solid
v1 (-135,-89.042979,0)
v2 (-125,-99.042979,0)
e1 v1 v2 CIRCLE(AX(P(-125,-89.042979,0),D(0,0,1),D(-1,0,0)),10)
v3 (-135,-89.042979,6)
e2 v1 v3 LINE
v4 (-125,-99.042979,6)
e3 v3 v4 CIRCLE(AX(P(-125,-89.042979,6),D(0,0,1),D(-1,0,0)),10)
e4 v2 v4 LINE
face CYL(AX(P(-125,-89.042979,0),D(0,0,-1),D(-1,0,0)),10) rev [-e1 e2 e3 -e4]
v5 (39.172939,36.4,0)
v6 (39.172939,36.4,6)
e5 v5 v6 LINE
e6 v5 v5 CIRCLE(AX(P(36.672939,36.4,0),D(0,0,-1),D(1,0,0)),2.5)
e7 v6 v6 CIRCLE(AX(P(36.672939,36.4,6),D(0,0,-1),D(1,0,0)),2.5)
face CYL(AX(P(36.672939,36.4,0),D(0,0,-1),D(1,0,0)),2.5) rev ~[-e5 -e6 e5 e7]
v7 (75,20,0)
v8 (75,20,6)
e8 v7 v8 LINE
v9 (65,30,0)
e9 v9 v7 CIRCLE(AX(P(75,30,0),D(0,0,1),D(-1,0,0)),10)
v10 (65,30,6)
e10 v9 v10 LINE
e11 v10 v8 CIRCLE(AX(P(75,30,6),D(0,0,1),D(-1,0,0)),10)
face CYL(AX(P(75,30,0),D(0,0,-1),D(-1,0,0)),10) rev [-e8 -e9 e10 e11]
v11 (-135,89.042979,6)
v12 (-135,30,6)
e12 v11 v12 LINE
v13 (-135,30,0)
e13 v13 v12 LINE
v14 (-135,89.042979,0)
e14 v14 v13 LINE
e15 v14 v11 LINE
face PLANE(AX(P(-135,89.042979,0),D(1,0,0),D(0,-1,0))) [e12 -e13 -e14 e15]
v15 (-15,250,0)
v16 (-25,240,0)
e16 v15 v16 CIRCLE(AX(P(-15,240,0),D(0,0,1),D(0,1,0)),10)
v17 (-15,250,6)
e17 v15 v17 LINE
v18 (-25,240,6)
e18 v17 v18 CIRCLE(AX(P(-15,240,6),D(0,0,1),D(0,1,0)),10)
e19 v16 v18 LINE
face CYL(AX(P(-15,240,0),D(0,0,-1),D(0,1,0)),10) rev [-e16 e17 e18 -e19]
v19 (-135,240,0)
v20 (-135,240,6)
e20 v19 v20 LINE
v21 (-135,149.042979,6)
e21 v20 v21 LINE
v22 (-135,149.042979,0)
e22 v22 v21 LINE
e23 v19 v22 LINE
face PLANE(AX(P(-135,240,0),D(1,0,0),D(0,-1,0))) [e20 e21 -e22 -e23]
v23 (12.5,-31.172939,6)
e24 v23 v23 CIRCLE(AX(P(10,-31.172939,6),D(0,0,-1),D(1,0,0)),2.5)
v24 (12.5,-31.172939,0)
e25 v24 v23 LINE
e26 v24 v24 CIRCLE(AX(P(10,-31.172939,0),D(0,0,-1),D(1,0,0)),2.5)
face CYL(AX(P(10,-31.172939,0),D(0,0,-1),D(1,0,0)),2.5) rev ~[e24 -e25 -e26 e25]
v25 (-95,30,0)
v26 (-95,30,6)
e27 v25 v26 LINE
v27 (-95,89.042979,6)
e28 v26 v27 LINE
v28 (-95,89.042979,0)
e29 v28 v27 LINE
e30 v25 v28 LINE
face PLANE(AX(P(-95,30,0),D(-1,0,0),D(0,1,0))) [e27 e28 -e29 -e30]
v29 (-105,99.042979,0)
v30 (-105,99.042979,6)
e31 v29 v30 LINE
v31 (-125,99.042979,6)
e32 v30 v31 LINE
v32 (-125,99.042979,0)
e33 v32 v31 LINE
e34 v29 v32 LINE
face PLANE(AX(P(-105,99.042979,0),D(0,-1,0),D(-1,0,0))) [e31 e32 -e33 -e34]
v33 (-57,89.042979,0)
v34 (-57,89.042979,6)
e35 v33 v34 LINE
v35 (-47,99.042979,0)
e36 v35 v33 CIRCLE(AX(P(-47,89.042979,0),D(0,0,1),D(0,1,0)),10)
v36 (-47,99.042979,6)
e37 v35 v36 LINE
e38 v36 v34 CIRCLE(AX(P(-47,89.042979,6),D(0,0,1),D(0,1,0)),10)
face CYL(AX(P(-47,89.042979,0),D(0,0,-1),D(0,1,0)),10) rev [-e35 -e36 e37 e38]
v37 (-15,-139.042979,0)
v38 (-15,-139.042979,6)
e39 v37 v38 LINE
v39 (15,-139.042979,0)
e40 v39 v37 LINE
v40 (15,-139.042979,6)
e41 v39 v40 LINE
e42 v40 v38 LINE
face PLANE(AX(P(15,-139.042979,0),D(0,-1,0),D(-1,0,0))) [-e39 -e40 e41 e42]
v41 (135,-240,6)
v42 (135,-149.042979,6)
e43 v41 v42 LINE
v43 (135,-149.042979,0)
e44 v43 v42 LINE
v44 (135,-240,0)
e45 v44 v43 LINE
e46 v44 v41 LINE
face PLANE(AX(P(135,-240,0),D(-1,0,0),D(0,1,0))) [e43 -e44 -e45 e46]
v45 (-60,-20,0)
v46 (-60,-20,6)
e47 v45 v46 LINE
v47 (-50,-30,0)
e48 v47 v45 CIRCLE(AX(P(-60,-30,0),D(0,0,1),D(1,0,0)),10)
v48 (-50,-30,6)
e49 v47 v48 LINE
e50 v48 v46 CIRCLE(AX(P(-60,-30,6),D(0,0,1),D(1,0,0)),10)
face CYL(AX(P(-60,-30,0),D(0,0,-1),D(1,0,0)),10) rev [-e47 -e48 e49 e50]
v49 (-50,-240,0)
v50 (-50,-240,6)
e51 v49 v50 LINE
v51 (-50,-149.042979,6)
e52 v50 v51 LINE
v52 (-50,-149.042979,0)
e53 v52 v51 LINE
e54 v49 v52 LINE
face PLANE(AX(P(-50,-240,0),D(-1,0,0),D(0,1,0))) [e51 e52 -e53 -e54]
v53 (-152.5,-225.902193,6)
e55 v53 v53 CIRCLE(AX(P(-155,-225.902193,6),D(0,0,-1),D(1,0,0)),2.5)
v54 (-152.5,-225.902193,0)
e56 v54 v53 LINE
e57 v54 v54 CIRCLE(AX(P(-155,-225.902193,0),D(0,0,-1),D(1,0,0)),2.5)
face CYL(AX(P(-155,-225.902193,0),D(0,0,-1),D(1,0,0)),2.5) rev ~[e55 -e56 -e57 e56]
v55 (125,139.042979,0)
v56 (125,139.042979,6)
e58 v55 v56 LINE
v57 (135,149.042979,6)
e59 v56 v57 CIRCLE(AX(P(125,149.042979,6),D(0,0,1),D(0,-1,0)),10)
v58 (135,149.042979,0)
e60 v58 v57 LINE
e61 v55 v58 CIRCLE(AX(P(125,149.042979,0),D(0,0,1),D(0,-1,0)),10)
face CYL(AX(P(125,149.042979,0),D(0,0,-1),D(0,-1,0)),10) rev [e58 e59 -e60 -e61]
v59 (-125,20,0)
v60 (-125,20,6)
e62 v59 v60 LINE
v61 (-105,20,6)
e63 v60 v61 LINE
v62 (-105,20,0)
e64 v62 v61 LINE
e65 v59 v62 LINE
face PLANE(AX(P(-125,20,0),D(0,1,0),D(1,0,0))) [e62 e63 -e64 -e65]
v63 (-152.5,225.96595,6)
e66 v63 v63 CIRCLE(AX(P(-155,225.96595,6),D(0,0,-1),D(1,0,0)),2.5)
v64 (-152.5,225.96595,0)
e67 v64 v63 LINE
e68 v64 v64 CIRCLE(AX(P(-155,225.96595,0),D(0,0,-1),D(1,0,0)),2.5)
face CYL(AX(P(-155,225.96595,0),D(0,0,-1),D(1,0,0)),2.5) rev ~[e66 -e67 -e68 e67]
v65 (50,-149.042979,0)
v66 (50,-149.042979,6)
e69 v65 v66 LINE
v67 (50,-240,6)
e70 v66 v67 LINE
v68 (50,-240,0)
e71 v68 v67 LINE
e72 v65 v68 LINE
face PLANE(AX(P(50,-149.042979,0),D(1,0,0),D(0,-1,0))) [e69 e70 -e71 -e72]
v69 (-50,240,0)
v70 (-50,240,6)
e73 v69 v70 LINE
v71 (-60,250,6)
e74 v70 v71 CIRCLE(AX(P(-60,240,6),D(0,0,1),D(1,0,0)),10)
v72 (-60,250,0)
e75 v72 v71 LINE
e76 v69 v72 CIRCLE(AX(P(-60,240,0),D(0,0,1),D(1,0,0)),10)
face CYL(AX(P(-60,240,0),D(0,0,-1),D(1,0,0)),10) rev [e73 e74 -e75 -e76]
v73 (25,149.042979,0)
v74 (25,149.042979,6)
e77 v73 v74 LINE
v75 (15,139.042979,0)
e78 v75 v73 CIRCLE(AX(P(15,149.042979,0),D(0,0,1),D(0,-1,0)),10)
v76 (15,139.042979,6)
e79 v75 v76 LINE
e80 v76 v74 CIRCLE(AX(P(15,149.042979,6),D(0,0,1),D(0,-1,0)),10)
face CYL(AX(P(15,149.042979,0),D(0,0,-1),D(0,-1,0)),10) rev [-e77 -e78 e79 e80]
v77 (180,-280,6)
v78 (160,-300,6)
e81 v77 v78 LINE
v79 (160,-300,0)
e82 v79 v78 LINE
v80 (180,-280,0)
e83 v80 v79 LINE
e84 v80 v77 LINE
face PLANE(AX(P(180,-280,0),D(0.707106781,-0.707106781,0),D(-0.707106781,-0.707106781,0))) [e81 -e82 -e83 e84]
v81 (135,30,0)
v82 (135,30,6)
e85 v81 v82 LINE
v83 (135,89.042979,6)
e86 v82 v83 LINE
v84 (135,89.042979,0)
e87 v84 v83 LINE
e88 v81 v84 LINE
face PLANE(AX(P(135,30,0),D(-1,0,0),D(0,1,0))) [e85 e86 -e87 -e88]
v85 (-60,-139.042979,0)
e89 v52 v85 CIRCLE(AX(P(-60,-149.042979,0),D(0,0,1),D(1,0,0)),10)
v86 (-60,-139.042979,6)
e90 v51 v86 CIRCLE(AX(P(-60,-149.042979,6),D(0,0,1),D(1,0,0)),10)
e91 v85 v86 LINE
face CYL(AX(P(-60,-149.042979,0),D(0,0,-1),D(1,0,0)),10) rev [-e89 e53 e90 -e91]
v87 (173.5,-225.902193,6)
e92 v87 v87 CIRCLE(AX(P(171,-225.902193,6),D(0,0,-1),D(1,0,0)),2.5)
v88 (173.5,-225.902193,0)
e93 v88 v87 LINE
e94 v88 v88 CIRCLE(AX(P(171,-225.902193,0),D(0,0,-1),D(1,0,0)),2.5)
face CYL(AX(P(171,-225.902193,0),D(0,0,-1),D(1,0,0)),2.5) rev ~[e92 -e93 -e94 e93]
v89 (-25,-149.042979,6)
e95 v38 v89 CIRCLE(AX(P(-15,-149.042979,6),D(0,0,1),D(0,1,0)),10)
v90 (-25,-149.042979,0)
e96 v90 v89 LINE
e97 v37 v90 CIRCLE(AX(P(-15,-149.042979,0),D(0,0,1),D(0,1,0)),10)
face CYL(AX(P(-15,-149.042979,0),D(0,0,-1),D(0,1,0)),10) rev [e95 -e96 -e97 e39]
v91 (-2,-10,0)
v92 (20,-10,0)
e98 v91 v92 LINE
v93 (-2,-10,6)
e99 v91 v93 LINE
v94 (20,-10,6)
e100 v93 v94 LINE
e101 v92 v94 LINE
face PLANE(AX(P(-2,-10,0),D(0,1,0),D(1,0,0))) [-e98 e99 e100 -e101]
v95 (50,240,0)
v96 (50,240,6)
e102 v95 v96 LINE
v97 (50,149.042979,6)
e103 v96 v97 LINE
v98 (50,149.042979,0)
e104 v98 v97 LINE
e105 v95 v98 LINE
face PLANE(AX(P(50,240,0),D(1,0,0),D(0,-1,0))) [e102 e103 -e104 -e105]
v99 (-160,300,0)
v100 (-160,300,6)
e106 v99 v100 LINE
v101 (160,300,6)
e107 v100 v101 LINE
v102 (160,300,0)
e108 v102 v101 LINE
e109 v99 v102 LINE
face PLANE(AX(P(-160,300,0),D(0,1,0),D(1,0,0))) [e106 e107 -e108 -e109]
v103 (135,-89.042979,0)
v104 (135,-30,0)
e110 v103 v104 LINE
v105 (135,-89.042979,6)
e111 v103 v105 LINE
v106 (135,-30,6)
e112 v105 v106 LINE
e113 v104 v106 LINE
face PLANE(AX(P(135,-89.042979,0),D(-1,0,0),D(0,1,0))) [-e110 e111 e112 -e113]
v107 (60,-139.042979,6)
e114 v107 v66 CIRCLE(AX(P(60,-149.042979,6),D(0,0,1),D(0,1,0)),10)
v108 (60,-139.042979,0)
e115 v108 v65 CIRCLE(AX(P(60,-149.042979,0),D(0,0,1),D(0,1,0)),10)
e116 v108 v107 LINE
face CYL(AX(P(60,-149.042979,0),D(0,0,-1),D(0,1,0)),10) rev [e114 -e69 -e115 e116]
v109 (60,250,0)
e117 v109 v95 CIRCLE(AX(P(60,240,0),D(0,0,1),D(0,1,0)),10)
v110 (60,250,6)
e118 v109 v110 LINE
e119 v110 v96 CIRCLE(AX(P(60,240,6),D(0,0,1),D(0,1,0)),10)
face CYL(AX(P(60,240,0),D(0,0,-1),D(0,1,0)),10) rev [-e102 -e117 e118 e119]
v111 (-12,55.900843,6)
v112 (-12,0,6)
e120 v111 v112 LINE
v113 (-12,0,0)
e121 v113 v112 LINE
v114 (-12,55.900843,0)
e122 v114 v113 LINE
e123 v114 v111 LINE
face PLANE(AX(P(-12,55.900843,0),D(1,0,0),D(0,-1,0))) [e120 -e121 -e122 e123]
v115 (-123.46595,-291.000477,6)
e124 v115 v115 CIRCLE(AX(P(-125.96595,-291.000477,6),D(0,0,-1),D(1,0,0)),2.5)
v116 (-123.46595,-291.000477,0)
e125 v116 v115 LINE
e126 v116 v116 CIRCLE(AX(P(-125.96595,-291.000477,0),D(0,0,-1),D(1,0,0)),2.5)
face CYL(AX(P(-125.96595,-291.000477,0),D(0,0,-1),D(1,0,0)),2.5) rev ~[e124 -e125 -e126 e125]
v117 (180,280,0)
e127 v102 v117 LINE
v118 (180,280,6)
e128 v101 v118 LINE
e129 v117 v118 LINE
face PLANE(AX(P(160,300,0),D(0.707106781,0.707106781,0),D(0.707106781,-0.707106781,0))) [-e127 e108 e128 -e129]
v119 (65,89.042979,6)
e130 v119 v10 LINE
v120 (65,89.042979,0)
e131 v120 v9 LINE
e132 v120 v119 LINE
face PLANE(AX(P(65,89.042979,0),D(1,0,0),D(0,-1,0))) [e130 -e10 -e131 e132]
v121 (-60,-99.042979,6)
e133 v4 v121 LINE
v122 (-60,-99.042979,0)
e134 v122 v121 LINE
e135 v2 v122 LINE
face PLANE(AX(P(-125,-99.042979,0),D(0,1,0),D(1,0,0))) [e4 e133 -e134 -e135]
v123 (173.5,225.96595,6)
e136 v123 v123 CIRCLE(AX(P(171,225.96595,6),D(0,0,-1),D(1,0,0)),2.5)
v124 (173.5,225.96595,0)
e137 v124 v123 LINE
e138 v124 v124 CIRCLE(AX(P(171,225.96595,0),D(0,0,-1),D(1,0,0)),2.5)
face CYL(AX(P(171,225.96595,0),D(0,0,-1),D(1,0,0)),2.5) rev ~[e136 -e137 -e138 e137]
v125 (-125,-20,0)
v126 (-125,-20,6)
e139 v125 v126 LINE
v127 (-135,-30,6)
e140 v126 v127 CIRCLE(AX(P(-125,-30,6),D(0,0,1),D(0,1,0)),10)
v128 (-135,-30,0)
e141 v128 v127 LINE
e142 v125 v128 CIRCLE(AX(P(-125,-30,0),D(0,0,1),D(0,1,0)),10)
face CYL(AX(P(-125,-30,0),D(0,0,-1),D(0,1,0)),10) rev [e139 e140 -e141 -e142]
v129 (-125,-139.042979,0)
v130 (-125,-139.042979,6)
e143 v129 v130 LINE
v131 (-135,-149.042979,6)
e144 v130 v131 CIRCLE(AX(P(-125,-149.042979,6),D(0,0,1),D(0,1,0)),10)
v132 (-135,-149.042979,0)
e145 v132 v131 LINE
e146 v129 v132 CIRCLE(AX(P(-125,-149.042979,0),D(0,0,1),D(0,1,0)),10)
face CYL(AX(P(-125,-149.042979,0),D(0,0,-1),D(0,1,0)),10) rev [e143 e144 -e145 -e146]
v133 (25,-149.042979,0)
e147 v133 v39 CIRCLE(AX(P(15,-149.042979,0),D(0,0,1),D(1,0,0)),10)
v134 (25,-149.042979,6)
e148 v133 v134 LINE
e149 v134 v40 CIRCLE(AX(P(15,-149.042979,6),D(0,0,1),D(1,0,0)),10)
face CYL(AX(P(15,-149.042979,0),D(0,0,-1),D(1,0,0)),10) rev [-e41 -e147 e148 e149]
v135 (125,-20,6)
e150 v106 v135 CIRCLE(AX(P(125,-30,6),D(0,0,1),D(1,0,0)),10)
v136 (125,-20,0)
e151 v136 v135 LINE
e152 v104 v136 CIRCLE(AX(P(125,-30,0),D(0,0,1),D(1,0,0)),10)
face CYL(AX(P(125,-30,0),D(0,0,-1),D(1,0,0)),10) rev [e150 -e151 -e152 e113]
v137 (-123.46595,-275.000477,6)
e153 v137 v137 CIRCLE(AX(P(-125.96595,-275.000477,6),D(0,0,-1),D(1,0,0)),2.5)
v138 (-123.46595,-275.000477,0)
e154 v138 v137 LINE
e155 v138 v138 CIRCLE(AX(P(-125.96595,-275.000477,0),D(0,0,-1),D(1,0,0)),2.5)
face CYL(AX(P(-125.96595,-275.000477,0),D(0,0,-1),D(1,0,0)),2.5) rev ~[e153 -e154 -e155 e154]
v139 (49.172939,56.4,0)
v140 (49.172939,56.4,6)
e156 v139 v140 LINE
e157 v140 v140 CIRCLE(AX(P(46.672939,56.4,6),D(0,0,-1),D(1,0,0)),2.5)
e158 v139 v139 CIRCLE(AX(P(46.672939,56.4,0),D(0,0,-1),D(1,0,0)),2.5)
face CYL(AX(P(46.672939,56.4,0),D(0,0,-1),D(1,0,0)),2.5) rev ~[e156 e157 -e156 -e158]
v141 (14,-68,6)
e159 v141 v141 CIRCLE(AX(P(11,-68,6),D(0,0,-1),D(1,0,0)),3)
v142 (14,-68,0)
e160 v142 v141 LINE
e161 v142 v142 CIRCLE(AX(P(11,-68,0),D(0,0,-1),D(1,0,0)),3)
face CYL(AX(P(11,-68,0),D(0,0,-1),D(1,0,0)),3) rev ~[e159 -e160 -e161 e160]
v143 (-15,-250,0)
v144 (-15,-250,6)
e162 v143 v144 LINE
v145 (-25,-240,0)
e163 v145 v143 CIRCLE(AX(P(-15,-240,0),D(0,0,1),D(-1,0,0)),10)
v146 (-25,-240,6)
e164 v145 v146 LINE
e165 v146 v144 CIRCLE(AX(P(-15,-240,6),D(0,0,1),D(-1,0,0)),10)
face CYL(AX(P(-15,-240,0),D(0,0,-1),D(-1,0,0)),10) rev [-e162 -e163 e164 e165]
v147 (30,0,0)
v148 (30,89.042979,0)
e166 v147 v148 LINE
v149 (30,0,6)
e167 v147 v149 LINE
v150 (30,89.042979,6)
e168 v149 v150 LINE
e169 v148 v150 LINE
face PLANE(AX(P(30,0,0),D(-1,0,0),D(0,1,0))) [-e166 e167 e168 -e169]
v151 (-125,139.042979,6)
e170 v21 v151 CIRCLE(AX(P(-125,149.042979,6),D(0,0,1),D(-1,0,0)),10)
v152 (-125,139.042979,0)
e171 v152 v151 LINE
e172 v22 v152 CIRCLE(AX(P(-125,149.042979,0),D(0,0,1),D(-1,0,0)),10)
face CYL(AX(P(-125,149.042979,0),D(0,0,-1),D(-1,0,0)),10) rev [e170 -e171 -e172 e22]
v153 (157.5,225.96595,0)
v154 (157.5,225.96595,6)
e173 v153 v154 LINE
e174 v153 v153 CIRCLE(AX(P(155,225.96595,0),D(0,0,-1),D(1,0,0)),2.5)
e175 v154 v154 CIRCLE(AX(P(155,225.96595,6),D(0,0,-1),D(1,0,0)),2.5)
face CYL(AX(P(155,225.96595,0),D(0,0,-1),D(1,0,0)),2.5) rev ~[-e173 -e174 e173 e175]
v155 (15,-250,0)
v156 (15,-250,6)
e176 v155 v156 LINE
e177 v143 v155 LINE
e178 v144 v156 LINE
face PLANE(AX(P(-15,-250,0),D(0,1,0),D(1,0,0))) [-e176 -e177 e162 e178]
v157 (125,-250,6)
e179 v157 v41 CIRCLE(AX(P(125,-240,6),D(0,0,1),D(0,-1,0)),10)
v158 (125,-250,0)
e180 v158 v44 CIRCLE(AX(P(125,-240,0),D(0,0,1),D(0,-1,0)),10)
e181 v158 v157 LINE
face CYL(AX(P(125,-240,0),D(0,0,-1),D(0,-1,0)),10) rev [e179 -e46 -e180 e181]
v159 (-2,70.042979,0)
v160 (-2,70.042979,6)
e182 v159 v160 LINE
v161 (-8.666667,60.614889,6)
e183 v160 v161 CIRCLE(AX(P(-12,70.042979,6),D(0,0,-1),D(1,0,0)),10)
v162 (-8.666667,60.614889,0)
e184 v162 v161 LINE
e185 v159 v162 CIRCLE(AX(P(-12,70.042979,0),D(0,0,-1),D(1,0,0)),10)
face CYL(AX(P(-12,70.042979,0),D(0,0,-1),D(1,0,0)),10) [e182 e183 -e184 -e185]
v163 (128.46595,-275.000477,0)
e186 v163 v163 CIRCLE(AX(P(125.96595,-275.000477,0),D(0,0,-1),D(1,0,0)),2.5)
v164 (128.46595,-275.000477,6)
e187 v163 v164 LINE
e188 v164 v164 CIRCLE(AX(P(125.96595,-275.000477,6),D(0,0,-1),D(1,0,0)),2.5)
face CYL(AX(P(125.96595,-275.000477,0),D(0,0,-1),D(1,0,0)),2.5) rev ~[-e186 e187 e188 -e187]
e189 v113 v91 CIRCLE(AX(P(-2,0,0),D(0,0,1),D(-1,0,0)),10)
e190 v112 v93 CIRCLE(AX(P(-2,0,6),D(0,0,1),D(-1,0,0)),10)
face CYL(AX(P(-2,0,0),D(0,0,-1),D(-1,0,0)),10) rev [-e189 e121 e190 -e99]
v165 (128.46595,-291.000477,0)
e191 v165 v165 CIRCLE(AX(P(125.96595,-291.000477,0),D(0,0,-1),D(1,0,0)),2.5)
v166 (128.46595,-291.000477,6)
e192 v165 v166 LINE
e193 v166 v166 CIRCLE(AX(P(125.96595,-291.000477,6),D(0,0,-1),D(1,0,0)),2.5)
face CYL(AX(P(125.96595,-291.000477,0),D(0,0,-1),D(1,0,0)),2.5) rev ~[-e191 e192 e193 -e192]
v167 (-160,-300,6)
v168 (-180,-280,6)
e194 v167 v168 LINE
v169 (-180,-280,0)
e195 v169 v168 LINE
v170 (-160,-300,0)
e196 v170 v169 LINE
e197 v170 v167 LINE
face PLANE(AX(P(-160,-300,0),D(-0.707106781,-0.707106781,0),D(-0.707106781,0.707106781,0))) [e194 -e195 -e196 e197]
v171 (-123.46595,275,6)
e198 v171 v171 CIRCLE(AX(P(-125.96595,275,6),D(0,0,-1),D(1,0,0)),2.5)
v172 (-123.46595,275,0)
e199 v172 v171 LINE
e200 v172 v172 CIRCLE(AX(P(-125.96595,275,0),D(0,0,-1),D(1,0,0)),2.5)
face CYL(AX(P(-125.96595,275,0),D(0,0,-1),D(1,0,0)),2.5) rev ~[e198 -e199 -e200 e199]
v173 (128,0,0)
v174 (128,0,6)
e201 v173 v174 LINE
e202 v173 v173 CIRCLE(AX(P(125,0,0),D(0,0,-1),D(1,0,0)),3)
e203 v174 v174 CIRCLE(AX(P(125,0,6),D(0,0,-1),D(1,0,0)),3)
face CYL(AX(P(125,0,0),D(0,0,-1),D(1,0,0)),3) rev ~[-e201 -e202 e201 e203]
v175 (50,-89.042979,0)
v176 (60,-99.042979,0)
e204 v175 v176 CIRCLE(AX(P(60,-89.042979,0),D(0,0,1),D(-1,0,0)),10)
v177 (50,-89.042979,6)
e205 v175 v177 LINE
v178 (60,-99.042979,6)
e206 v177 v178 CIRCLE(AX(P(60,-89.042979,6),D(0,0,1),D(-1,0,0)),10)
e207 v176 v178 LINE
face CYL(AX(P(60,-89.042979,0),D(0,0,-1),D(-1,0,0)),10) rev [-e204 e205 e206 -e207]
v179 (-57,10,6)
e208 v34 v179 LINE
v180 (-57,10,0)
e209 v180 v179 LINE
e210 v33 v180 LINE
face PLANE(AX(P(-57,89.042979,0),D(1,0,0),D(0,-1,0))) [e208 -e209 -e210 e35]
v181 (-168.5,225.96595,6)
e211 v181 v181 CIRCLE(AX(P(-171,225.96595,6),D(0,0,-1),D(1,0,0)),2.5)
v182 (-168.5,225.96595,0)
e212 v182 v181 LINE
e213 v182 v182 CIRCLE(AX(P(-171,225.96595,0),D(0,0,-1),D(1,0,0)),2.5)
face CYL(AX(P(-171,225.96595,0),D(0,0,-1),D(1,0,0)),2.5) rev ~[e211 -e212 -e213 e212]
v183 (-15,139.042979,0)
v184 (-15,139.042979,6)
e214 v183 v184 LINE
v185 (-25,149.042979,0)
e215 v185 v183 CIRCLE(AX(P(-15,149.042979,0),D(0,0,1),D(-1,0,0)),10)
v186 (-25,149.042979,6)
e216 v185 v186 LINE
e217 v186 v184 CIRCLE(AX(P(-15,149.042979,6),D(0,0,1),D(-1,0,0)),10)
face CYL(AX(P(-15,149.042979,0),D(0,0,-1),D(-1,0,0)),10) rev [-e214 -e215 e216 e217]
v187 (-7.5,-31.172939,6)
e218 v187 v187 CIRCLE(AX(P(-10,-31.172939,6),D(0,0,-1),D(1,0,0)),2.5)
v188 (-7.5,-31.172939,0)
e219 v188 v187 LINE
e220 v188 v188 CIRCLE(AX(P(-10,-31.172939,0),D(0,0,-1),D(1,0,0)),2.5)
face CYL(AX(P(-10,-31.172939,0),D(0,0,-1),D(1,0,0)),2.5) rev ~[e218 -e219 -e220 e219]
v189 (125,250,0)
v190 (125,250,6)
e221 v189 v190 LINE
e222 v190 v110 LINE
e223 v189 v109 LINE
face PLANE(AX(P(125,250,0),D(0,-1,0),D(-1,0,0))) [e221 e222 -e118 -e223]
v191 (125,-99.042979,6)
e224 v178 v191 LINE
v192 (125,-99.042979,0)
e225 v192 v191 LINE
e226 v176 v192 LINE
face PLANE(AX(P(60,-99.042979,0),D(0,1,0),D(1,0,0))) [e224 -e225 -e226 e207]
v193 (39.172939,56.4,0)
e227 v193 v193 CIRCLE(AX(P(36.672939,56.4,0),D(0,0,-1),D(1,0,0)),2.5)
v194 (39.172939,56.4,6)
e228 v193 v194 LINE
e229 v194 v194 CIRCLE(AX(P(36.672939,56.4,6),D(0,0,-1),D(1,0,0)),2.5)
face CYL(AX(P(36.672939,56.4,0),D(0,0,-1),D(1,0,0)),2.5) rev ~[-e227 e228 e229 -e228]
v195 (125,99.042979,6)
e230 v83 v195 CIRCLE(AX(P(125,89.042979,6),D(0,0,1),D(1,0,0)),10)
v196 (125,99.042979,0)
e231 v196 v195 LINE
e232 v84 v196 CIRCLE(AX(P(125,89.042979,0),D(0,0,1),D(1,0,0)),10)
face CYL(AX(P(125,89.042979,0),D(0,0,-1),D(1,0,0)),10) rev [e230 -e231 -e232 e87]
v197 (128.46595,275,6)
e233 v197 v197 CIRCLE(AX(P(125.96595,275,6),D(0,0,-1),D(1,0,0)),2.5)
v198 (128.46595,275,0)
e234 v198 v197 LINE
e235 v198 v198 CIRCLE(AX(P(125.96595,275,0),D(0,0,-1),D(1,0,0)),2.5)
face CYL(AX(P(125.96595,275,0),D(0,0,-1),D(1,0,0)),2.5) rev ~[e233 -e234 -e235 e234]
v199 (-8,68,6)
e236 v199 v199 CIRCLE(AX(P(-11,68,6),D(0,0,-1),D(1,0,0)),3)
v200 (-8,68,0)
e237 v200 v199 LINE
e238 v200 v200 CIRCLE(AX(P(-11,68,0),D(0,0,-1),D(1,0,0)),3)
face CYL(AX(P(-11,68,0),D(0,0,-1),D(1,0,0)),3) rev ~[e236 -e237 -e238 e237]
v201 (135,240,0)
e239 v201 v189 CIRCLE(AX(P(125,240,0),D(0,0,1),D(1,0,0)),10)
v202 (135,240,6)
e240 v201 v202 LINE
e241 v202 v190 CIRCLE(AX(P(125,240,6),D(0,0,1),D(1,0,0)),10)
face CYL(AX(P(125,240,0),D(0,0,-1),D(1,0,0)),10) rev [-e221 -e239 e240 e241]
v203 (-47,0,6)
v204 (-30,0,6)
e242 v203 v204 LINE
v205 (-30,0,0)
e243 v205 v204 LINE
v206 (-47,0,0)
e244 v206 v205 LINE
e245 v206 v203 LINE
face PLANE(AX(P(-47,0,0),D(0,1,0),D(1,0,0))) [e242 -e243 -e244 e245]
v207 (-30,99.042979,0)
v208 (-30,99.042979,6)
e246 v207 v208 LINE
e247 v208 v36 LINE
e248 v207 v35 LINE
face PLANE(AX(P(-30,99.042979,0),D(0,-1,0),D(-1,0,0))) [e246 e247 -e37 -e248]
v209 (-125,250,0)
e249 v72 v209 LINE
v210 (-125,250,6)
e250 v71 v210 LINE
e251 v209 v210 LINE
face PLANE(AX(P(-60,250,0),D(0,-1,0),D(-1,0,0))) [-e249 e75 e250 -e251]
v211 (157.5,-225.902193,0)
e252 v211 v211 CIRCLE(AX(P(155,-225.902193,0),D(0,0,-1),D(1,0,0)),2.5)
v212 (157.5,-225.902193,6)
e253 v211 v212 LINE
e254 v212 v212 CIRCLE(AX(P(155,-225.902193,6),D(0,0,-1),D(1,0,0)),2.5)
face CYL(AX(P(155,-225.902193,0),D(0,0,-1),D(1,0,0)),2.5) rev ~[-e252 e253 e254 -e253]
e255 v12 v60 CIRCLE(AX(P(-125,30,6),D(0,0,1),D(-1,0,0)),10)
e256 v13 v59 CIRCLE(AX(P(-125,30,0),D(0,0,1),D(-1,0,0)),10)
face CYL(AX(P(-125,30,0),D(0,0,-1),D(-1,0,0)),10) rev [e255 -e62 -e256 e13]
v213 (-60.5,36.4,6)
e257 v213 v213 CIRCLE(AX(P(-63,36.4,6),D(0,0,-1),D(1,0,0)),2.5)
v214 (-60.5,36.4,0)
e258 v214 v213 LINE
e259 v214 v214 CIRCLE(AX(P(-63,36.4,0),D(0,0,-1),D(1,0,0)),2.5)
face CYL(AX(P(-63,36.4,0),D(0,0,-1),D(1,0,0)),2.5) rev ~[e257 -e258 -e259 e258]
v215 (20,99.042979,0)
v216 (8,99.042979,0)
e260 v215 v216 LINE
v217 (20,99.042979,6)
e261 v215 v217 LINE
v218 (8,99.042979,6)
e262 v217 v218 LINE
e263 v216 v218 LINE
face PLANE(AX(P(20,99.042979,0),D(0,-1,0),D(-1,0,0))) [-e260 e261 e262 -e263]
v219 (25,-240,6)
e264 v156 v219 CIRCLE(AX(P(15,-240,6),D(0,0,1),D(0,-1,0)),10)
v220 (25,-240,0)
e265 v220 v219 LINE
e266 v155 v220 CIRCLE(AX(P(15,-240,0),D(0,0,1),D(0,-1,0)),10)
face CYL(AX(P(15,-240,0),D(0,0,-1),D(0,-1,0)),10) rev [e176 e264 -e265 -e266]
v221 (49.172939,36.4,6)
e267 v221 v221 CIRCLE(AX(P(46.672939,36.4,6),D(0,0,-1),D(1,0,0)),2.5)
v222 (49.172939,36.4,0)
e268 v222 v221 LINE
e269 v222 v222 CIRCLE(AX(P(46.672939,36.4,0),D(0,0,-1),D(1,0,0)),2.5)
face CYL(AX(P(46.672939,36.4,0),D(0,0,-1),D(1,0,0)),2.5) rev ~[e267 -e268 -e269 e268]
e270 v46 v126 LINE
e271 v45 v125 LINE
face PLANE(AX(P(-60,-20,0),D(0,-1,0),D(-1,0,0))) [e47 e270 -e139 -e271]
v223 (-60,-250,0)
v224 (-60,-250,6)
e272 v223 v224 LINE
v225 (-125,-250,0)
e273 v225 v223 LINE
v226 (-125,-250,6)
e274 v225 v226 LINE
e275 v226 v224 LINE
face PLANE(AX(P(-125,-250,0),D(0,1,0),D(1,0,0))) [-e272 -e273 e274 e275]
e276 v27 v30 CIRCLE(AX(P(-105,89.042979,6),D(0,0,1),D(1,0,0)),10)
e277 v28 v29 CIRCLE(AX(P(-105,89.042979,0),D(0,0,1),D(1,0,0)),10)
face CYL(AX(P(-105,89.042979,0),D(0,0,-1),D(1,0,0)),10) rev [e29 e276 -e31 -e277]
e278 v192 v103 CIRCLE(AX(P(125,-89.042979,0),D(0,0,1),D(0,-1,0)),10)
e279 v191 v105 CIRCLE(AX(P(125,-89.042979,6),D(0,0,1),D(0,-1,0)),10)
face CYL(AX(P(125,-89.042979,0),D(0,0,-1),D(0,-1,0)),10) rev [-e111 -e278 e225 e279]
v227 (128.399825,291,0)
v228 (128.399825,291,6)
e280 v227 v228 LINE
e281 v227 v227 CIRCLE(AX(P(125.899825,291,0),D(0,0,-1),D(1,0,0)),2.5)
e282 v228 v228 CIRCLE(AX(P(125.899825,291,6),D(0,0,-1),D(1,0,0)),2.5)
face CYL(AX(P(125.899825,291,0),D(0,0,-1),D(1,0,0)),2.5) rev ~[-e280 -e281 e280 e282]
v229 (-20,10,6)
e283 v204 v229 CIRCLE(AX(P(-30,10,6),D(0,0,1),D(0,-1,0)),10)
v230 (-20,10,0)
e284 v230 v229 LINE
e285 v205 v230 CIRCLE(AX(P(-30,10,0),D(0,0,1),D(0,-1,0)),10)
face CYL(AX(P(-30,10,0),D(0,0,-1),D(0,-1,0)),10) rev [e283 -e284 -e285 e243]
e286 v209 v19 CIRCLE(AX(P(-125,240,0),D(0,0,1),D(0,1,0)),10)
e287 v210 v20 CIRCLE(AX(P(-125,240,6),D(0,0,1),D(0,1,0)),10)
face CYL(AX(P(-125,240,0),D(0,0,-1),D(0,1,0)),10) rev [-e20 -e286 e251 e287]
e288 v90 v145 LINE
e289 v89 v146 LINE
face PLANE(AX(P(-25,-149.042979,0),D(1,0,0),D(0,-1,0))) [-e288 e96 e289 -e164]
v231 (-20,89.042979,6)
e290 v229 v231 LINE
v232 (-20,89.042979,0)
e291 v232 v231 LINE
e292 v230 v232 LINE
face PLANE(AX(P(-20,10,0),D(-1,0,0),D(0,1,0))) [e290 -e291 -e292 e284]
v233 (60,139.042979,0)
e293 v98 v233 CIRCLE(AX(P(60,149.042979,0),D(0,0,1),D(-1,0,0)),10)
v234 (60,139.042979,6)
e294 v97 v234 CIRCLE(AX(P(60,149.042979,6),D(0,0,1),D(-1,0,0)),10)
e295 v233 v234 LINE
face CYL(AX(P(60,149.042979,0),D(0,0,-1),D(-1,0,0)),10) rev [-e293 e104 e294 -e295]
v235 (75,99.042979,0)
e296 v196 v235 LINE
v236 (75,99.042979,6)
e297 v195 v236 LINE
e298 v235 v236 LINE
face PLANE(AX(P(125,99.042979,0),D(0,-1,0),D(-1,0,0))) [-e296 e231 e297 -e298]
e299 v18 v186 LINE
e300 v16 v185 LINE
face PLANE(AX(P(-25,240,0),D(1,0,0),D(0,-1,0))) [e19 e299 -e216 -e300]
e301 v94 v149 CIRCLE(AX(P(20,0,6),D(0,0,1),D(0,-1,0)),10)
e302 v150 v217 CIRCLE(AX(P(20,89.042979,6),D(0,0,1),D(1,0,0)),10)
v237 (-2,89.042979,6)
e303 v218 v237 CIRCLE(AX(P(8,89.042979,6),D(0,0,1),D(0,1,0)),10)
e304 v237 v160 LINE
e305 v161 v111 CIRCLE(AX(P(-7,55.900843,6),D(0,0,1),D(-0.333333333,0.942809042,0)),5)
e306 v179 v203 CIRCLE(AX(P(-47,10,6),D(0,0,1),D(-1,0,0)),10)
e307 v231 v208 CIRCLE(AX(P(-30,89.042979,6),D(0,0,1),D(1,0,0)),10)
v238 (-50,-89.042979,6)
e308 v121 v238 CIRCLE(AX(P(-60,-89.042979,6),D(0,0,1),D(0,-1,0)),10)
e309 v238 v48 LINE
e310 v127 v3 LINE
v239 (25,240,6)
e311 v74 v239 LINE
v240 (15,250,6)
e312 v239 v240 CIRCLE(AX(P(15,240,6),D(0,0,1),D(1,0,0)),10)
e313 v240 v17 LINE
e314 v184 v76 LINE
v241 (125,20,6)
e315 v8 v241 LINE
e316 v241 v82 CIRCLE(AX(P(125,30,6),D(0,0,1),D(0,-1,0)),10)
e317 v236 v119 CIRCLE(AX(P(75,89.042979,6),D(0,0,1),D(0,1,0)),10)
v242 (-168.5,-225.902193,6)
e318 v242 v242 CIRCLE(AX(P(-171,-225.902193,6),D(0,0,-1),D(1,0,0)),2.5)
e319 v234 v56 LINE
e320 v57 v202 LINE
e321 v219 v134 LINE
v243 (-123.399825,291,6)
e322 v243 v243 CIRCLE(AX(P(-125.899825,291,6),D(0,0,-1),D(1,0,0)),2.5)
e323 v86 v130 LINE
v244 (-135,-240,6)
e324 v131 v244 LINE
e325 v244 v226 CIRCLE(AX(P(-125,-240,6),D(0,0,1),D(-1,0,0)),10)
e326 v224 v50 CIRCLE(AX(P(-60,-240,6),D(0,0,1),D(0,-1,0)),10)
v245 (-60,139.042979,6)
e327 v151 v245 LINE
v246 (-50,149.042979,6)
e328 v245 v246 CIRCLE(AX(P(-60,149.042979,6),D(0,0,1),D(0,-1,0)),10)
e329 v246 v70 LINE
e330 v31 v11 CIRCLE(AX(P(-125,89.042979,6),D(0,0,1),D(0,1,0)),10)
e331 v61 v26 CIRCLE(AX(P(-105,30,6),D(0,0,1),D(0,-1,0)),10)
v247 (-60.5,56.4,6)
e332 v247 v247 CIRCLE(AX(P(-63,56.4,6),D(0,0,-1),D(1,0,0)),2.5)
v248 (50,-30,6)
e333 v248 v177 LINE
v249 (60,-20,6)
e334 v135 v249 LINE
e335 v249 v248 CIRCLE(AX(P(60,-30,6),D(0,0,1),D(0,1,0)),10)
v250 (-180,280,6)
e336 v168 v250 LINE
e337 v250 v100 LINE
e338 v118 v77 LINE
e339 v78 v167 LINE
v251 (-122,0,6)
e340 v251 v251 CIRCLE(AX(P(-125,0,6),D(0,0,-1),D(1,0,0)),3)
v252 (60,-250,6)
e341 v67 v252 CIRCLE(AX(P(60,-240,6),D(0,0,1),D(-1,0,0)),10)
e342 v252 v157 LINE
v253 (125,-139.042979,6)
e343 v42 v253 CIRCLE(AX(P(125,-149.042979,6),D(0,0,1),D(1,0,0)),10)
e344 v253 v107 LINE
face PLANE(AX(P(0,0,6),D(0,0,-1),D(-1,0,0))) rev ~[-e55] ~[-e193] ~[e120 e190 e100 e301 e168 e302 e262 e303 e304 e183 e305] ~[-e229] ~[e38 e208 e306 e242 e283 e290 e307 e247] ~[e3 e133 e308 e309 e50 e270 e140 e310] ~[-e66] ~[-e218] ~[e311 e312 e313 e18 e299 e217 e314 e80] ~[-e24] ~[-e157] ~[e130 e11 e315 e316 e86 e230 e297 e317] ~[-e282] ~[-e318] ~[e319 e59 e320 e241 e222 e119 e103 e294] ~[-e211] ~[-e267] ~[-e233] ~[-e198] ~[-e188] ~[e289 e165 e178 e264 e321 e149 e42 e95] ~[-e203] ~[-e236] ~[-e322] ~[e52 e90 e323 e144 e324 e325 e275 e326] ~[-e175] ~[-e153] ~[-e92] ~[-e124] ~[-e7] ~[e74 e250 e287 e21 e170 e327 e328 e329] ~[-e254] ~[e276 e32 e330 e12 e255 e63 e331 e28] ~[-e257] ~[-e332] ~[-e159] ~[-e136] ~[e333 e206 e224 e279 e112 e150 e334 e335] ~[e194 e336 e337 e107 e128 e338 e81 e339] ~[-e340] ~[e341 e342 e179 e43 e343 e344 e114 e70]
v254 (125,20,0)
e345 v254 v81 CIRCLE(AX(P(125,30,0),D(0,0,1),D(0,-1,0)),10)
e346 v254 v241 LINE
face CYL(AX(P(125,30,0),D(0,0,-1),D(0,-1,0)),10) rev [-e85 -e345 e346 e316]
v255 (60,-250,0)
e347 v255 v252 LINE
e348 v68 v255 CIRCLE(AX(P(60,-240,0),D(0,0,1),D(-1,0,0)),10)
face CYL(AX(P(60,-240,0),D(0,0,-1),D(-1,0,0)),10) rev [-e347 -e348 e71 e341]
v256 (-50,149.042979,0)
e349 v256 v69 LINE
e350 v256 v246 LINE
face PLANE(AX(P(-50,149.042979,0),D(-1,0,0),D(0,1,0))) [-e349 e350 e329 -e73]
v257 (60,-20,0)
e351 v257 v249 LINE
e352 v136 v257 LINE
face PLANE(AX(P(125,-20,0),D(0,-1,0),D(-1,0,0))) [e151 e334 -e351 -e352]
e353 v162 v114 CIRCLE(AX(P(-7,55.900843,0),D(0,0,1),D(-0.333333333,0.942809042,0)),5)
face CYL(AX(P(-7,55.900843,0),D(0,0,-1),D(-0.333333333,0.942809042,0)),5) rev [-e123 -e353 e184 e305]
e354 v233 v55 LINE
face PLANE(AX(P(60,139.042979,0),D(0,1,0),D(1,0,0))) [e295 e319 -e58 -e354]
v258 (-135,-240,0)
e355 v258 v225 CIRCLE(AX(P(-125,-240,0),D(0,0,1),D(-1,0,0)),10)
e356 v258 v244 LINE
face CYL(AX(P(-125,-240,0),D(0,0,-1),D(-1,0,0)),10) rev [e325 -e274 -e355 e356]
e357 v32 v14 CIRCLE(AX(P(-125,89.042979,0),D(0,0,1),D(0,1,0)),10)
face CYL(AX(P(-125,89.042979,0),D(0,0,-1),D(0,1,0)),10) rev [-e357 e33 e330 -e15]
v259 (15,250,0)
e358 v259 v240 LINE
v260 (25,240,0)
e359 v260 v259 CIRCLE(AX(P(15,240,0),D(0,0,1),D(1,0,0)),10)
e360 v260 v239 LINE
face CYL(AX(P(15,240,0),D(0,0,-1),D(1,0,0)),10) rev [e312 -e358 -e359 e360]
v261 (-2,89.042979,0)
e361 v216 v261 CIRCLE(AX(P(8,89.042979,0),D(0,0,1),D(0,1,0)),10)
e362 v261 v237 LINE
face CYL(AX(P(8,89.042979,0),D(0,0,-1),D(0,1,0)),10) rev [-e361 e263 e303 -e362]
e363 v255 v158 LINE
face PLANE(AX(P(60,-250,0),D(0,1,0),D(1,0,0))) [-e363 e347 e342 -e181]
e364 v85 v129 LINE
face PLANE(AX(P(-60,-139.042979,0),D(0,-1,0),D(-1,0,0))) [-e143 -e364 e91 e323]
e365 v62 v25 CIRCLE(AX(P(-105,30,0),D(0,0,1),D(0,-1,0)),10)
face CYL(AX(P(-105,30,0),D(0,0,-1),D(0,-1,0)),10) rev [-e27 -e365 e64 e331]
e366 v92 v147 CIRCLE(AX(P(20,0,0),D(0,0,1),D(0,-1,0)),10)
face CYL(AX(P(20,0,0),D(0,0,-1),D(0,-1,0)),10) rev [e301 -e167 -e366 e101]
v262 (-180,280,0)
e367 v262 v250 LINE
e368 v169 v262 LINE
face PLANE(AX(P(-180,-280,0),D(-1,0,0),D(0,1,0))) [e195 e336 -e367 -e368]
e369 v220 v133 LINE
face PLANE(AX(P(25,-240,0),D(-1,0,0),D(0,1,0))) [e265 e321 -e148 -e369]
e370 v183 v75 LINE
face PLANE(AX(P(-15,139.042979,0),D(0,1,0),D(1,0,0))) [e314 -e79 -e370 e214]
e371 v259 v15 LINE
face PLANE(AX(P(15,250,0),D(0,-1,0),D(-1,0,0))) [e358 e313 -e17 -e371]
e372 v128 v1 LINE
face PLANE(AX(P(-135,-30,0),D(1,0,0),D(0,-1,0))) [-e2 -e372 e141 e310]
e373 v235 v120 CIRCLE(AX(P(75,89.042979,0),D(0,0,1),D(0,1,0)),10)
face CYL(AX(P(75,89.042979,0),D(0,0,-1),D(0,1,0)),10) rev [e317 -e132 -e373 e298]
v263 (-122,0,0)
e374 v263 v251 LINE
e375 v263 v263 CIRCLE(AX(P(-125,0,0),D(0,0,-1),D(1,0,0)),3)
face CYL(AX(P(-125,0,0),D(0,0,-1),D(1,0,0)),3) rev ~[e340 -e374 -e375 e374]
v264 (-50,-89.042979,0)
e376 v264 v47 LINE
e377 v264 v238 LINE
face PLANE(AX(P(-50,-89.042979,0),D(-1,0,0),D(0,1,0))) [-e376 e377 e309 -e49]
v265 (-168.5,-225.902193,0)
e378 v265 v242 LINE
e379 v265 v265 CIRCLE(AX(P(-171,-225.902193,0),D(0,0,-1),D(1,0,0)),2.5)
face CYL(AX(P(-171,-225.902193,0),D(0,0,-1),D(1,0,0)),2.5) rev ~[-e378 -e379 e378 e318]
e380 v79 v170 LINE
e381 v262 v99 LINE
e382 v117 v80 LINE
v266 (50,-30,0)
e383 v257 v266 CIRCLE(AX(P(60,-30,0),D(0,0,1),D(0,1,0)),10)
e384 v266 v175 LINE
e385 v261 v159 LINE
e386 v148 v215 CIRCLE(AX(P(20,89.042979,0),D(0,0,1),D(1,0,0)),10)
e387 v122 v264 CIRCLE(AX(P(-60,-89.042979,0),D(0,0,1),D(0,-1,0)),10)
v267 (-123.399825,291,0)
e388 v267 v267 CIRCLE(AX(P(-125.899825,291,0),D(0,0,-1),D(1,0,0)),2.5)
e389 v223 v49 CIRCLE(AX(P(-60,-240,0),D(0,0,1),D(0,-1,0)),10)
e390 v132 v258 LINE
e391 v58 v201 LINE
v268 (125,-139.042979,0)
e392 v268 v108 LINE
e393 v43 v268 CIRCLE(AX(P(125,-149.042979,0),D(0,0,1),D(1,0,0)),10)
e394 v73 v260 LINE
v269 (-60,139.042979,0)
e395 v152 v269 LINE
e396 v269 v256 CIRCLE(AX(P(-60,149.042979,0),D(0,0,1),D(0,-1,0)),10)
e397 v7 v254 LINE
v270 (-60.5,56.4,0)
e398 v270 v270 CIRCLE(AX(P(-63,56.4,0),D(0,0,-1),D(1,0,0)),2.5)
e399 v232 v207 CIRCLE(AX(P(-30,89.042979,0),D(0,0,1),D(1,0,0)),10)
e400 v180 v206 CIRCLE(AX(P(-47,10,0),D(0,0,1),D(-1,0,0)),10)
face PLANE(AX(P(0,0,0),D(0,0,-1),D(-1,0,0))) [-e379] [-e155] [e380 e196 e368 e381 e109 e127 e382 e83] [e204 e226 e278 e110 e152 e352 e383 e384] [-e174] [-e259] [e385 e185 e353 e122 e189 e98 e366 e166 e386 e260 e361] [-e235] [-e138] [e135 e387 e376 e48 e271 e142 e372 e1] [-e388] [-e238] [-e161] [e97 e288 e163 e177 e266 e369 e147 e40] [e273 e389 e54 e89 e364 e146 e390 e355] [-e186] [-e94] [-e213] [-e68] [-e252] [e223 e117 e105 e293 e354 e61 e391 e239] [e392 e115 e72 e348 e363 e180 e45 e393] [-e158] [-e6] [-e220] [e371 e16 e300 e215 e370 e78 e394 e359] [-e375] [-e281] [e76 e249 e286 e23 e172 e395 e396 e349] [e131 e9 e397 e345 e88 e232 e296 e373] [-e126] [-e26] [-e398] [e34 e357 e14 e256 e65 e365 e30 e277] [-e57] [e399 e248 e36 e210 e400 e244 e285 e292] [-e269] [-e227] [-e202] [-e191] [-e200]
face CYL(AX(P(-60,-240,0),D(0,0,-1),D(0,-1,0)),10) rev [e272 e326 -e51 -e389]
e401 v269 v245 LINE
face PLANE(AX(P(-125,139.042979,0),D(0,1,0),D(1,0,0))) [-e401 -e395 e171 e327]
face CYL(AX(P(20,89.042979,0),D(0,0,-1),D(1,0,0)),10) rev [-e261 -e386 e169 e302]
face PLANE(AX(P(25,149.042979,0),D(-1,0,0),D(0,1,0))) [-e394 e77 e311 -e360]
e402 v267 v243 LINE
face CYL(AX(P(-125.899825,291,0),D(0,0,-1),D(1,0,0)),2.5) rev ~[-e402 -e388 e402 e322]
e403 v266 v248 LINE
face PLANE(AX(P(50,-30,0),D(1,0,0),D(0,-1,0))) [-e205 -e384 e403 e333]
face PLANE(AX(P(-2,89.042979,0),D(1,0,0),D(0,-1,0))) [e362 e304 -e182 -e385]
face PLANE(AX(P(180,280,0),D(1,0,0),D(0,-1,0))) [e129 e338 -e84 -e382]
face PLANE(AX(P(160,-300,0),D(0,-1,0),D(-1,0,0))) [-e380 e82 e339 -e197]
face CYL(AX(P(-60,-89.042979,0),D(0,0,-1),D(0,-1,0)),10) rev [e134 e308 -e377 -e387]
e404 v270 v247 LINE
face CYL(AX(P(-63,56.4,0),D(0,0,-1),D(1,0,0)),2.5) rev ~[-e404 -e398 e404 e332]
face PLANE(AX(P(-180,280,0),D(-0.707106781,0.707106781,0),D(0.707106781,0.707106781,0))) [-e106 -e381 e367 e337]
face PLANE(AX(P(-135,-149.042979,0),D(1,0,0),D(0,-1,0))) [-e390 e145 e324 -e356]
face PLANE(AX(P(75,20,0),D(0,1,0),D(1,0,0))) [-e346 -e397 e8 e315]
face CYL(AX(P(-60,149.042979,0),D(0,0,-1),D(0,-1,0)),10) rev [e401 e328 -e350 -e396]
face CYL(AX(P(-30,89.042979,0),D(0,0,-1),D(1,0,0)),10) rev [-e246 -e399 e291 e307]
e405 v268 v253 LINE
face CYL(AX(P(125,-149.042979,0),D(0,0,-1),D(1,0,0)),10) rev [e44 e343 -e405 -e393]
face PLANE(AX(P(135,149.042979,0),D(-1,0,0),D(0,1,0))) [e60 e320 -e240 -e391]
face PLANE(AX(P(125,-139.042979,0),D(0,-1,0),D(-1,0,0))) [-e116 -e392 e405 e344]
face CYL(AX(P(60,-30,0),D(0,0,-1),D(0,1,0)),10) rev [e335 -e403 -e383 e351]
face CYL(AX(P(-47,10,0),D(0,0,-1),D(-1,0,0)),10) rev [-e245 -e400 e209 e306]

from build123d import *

# Parameters (mm, degrees)
SKETCH_1_R      = 2.5
SKETCH_1_R_2    = 3
EXTRUDE_1_DEPTH = 6


with BuildPart() as part:
    # 草图1 → 凸台-拉伸1 (new body)
    with BuildSketch(Plane(origin=(0, 0, 0), x_dir=(-1, 0, 0), z_dir=(0, 0, -1))):
        Polygon((160, -300), (180, -280), (180, 280), (160, 300), (-160, 300), (-180, 280), (-180, -280), (-160, -300), align=None)
        with Locations(Location((-36.672939041, 56.4, 0), (0, 0, 180))):
            Circle(SKETCH_1_R, mode=Mode.SUBTRACT)
        with Locations(Location((-10, -31.172939041, 0), (0, 0, 180))):
            Circle(SKETCH_1_R, mode=Mode.SUBTRACT)
        with Locations(Location((10, -31.172939041, 0), (0, 0, 180))):
            Circle(SKETCH_1_R, mode=Mode.SUBTRACT)
        with Locations(Location((-171, 225.965949669, 0), (0, 0, 180))):
            Circle(SKETCH_1_R, mode=Mode.SUBTRACT)
        with Locations(Location((-155, 225.965949669, 0), (0, 0, 180))):
            Circle(SKETCH_1_R, mode=Mode.SUBTRACT)
        with Locations(Location((-125.965949669, 275, 0), (0, 0, 180))):
            Circle(SKETCH_1_R, mode=Mode.SUBTRACT)
        with Locations(Location((-125.899824793, 291, 0), (0, 0, 180))):
            Circle(SKETCH_1_R, mode=Mode.SUBTRACT)
        with Locations(Location((-171, -225.902192547, 0), (0, 0, 180))):
            Circle(SKETCH_1_R, mode=Mode.SUBTRACT)
        with Locations(Location((-155, -225.902192547, 0), (0, 0, 180))):
            Circle(SKETCH_1_R, mode=Mode.SUBTRACT)
        with Locations(Location((-125.965949669, -275.000477451, 0), (0, 0, 180))):
            Circle(SKETCH_1_R, mode=Mode.SUBTRACT)
        with Locations(Location((-125.965949669, -291.000477451, 0), (0, 0, 180))):
            Circle(SKETCH_1_R, mode=Mode.SUBTRACT)
        with Locations(Location((125.899824793, 291, 0), (0, 0, 180))):
            Circle(SKETCH_1_R, mode=Mode.SUBTRACT)
        with Locations(Location((125.965949669, 275, 0), (0, 0, 180))):
            Circle(SKETCH_1_R, mode=Mode.SUBTRACT)
        with Locations(Location((171, 225.965949669, 0), (0, 0, 180))):
            Circle(SKETCH_1_R, mode=Mode.SUBTRACT)
        with Locations(Location((155, 225.965949669, 0), (0, 0, 180))):
            Circle(SKETCH_1_R, mode=Mode.SUBTRACT)
        with Locations(Location((171, -225.902192547, 0), (0, 0, 180))):
            Circle(SKETCH_1_R, mode=Mode.SUBTRACT)
        with Locations(Location((155, -225.902192547, 0), (0, 0, 180))):
            Circle(SKETCH_1_R, mode=Mode.SUBTRACT)
        with Locations(Location((125.965949669, -291.000477451, 0), (0, 0, 180))):
            Circle(SKETCH_1_R, mode=Mode.SUBTRACT)
        with Locations(Location((125.965949669, -275.000477451, 0), (0, 0, 180))):
            Circle(SKETCH_1_R, mode=Mode.SUBTRACT)
        with Locations(Location((63, 56.4, 0), (0, 0, 180))):
            Circle(SKETCH_1_R, mode=Mode.SUBTRACT)
        with Locations(Location((63, 36.4, 0), (0, 0, 180))):
            Circle(SKETCH_1_R, mode=Mode.SUBTRACT)
        with Locations(Location((-46.672939041, 56.4, 0), (0, 0, 180))):
            Circle(SKETCH_1_R, mode=Mode.SUBTRACT)
        with Locations(Location((-46.672939041, 36.4, 0), (0, 0, 180))):
            Circle(SKETCH_1_R, mode=Mode.SUBTRACT)
        with Locations(Location((-11, -68, 0), (0, 0, 180))):
            Circle(SKETCH_1_R_2, mode=Mode.SUBTRACT)
        with Locations(Location((11, 68, 0), (0, 0, 180))):
            Circle(SKETCH_1_R_2, mode=Mode.SUBTRACT)
        with Locations(Location((-125, 0, 0), (0, 0, 180))):
            Circle(SKETCH_1_R_2, mode=Mode.SUBTRACT)
        with Locations(Location((125, 0, 0), (0, 0, 180))):
            Circle(SKETCH_1_R_2, mode=Mode.SUBTRACT)
        with Locations(Location((-36.672939041, 36.4, 0), (0, 0, 180))):
            Circle(SKETCH_1_R, mode=Mode.SUBTRACT)
        with BuildLine():
            Line((20, 10), (20, 89.042978952))
            ThreePointArc((20, 89.042978952), (22.928932188, 96.114046764), (30, 99.042978952))
            Line((30, 99.042978952), (47, 99.042978952))
            ThreePointArc((47, 99.042978952), (54.071067812, 96.114046764), (57, 89.042978952))
            Line((57, 89.042978952), (57, 10))
            ThreePointArc((57, 10), (54.071067812, 2.928932188), (47, 0))
            Line((47, 0), (30, 0))
            ThreePointArc((30, 0), (22.928932188, 2.928932188), (20, 10))
        make_face(mode=Mode.SUBTRACT)
        with BuildLine():
            Line((2, -10), (-20, -10))
            ThreePointArc((-20, -10), (-27.071067812, -7.071067812), (-30, 0))
            Line((-30, 0), (-30, 89.042978952))
            ThreePointArc((-30, 89.042978952), (-27.071067812, 96.114046764), (-20, 99.042978952))
            Line((-20, 99.042978952), (-8, 99.042978952))
            ThreePointArc((-8, 99.042978952), (-0.928932188, 96.114046764), (2, 89.042978952))
            Line((2, 89.042978952), (2, 70.042978952))
            ThreePointArc((2, 70.042978952), (3.835034191, 64.26947626), (8.666666667, 60.614888536))
            ThreePointArc((8.666666667, 60.614888536), (11.082482905, 58.787594674), (12, 55.900843328))
            Line((12, 55.900843328), (12, 0))
            ThreePointArc((12, 0), (9.071067812, -7.071067812), (2, -10))
        make_face(mode=Mode.SUBTRACT)
        with BuildLine():
            Line((95, 30), (95, 89.042978952))
            ThreePointArc((95, 89.042978952), (97.928932188, 96.114046764), (105, 99.042978952))
            Line((105, 99.042978952), (125, 99.042978952))
            ThreePointArc((125, 99.042978952), (132.071067812, 96.114046764), (135, 89.042978952))
            Line((135, 89.042978952), (135, 30))
            ThreePointArc((135, 30), (132.071067812, 22.928932188), (125, 20))
            Line((125, 20), (105, 20))
            ThreePointArc((105, 20), (97.928932188, 22.928932188), (95, 30))
        make_face(mode=Mode.SUBTRACT)
        with BuildLine():
            Line((125, -250), (60, -250))
            ThreePointArc((60, -250), (52.928932188, -247.071067812), (50, -240))
            Line((50, -240), (50, -149.042978952))
            ThreePointArc((50, -149.042978952), (52.928932188, -141.97191114), (60, -139.042978952))
            Line((60, -139.042978952), (125, -139.042978952))
            ThreePointArc((125, -139.042978952), (132.071067812, -141.97191114), (135, -149.042978952))
            Line((135, -149.042978952), (135, -240))
            ThreePointArc((135, -240), (132.071067812, -247.071067812), (125, -250))
        make_face(mode=Mode.SUBTRACT)
        with BuildLine():
            Line((50, 149.042978952), (50, 240))
            ThreePointArc((50, 240), (52.928932188, 247.071067812), (60, 250))
            Line((60, 250), (125, 250))
            ThreePointArc((125, 250), (132.071067812, 247.071067812), (135, 240))
            Line((135, 240), (135, 149.042978952))
            ThreePointArc((135, 149.042978952), (132.071067812, 141.97191114), (125, 139.042978952))
            Line((125, 139.042978952), (60, 139.042978952))
            ThreePointArc((60, 139.042978952), (52.928932188, 141.97191114), (50, 149.042978952))
        make_face(mode=Mode.SUBTRACT)
        with BuildLine():
            Line((15, 139.042978952), (-15, 139.042978952))
            ThreePointArc((-15, 139.042978952), (-22.071067812, 141.97191114), (-25, 149.042978952))
            Line((-25, 149.042978952), (-25, 240))
            ThreePointArc((-25, 240), (-22.071067812, 247.071067812), (-15, 250))
            Line((-15, 250), (15, 250))
            ThreePointArc((15, 250), (22.071067812, 247.071067812), (25, 240))
            Line((25, 240), (25, 149.042978952))
            ThreePointArc((25, 149.042978952), (22.071067812, 141.97191114), (15, 139.042978952))
        make_face(mode=Mode.SUBTRACT)
        with BuildLine():
            Line((-15, -139.042978952), (15, -139.042978952))
            ThreePointArc((15, -139.042978952), (22.071067812, -141.97191114), (25, -149.042978952))
            Line((25, -149.042978952), (25, -240))
            ThreePointArc((25, -240), (22.071067812, -247.071067812), (15, -250))
            Line((15, -250), (-15, -250))
            ThreePointArc((-15, -250), (-22.071067812, -247.071067812), (-25, -240))
            Line((-25, -240), (-25, -149.042978952))
            ThreePointArc((-25, -149.042978952), (-22.071067812, -141.97191114), (-15, -139.042978952))
        make_face(mode=Mode.SUBTRACT)
        with BuildLine():
            Line((-50, -30), (-50, -89.042978952))
            ThreePointArc((-50, -89.042978952), (-52.928932188, -96.114046764), (-60, -99.042978952))
            Line((-60, -99.042978952), (-125, -99.042978952))
            ThreePointArc((-125, -99.042978952), (-132.071067812, -96.114046764), (-135, -89.042978952))
            Line((-135, -89.042978952), (-135, -30))
            ThreePointArc((-135, -30), (-132.071067812, -22.928932188), (-125, -20))
            Line((-125, -20), (-60, -20))
            ThreePointArc((-60, -20), (-52.928932188, -22.928932188), (-50, -30))
        make_face(mode=Mode.SUBTRACT)
        with BuildLine():
            Line((-50, -149.042978952), (-50, -240))
            ThreePointArc((-50, -240), (-52.928932188, -247.071067812), (-60, -250))
            Line((-60, -250), (-125, -250))
            ThreePointArc((-125, -250), (-132.071067812, -247.071067812), (-135, -240))
            Line((-135, -240), (-135, -149.042978952))
            ThreePointArc((-135, -149.042978952), (-132.071067812, -141.97191114), (-125, -139.042978952))
            Line((-125, -139.042978952), (-60, -139.042978952))
            ThreePointArc((-60, -139.042978952), (-52.928932188, -141.97191114), (-50, -149.042978952))
        make_face(mode=Mode.SUBTRACT)
        with BuildLine():
            Line((-75, 20), (-125, 20))
            ThreePointArc((-125, 20), (-132.071067812, 22.928932188), (-135, 30))
            Line((-135, 30), (-135, 89.042978952))
            ThreePointArc((-135, 89.042978952), (-132.071067812, 96.114046764), (-125, 99.042978952))
            Line((-125, 99.042978952), (-75, 99.042978952))
            ThreePointArc((-75, 99.042978952), (-67.928932188, 96.114046764), (-65, 89.042978952))
            Line((-65, 89.042978952), (-65, 30))
            ThreePointArc((-65, 30), (-67.928932188, 22.928932188), (-75, 20))
        make_face(mode=Mode.SUBTRACT)
        with BuildLine():
            Line((60, -20), (125, -20))
            ThreePointArc((125, -20), (132.071067812, -22.928932188), (135, -30))
            Line((135, -30), (135, -89.042978952))
            ThreePointArc((135, -89.042978952), (132.071067812, -96.114046764), (125, -99.042978952))
            Line((125, -99.042978952), (60, -99.042978952))
            ThreePointArc((60, -99.042978952), (52.928932188, -96.114046764), (50, -89.042978952))
            Line((50, -89.042978952), (50, -30))
            ThreePointArc((50, -30), (52.928932188, -22.928932188), (60, -20))
        make_face(mode=Mode.SUBTRACT)
        with BuildLine():
            Line((-125, 250), (-60, 250))
            ThreePointArc((-60, 250), (-52.928932188, 247.071067812), (-50, 240))
            Line((-50, 240), (-50, 149.042978952))
            ThreePointArc((-50, 149.042978952), (-52.928932188, 141.97191114), (-60, 139.042978952))
            Line((-60, 139.042978952), (-125, 139.042978952))
            ThreePointArc((-125, 139.042978952), (-132.071067812, 141.97191114), (-135, 149.042978952))
            Line((-135, 149.042978952), (-135, 240))
            ThreePointArc((-135, 240), (-132.071067812, 247.071067812), (-125, 250))
        make_face(mode=Mode.SUBTRACT)
    extrude(amount=-EXTRUDE_1_DEPTH)


solid = part.part
